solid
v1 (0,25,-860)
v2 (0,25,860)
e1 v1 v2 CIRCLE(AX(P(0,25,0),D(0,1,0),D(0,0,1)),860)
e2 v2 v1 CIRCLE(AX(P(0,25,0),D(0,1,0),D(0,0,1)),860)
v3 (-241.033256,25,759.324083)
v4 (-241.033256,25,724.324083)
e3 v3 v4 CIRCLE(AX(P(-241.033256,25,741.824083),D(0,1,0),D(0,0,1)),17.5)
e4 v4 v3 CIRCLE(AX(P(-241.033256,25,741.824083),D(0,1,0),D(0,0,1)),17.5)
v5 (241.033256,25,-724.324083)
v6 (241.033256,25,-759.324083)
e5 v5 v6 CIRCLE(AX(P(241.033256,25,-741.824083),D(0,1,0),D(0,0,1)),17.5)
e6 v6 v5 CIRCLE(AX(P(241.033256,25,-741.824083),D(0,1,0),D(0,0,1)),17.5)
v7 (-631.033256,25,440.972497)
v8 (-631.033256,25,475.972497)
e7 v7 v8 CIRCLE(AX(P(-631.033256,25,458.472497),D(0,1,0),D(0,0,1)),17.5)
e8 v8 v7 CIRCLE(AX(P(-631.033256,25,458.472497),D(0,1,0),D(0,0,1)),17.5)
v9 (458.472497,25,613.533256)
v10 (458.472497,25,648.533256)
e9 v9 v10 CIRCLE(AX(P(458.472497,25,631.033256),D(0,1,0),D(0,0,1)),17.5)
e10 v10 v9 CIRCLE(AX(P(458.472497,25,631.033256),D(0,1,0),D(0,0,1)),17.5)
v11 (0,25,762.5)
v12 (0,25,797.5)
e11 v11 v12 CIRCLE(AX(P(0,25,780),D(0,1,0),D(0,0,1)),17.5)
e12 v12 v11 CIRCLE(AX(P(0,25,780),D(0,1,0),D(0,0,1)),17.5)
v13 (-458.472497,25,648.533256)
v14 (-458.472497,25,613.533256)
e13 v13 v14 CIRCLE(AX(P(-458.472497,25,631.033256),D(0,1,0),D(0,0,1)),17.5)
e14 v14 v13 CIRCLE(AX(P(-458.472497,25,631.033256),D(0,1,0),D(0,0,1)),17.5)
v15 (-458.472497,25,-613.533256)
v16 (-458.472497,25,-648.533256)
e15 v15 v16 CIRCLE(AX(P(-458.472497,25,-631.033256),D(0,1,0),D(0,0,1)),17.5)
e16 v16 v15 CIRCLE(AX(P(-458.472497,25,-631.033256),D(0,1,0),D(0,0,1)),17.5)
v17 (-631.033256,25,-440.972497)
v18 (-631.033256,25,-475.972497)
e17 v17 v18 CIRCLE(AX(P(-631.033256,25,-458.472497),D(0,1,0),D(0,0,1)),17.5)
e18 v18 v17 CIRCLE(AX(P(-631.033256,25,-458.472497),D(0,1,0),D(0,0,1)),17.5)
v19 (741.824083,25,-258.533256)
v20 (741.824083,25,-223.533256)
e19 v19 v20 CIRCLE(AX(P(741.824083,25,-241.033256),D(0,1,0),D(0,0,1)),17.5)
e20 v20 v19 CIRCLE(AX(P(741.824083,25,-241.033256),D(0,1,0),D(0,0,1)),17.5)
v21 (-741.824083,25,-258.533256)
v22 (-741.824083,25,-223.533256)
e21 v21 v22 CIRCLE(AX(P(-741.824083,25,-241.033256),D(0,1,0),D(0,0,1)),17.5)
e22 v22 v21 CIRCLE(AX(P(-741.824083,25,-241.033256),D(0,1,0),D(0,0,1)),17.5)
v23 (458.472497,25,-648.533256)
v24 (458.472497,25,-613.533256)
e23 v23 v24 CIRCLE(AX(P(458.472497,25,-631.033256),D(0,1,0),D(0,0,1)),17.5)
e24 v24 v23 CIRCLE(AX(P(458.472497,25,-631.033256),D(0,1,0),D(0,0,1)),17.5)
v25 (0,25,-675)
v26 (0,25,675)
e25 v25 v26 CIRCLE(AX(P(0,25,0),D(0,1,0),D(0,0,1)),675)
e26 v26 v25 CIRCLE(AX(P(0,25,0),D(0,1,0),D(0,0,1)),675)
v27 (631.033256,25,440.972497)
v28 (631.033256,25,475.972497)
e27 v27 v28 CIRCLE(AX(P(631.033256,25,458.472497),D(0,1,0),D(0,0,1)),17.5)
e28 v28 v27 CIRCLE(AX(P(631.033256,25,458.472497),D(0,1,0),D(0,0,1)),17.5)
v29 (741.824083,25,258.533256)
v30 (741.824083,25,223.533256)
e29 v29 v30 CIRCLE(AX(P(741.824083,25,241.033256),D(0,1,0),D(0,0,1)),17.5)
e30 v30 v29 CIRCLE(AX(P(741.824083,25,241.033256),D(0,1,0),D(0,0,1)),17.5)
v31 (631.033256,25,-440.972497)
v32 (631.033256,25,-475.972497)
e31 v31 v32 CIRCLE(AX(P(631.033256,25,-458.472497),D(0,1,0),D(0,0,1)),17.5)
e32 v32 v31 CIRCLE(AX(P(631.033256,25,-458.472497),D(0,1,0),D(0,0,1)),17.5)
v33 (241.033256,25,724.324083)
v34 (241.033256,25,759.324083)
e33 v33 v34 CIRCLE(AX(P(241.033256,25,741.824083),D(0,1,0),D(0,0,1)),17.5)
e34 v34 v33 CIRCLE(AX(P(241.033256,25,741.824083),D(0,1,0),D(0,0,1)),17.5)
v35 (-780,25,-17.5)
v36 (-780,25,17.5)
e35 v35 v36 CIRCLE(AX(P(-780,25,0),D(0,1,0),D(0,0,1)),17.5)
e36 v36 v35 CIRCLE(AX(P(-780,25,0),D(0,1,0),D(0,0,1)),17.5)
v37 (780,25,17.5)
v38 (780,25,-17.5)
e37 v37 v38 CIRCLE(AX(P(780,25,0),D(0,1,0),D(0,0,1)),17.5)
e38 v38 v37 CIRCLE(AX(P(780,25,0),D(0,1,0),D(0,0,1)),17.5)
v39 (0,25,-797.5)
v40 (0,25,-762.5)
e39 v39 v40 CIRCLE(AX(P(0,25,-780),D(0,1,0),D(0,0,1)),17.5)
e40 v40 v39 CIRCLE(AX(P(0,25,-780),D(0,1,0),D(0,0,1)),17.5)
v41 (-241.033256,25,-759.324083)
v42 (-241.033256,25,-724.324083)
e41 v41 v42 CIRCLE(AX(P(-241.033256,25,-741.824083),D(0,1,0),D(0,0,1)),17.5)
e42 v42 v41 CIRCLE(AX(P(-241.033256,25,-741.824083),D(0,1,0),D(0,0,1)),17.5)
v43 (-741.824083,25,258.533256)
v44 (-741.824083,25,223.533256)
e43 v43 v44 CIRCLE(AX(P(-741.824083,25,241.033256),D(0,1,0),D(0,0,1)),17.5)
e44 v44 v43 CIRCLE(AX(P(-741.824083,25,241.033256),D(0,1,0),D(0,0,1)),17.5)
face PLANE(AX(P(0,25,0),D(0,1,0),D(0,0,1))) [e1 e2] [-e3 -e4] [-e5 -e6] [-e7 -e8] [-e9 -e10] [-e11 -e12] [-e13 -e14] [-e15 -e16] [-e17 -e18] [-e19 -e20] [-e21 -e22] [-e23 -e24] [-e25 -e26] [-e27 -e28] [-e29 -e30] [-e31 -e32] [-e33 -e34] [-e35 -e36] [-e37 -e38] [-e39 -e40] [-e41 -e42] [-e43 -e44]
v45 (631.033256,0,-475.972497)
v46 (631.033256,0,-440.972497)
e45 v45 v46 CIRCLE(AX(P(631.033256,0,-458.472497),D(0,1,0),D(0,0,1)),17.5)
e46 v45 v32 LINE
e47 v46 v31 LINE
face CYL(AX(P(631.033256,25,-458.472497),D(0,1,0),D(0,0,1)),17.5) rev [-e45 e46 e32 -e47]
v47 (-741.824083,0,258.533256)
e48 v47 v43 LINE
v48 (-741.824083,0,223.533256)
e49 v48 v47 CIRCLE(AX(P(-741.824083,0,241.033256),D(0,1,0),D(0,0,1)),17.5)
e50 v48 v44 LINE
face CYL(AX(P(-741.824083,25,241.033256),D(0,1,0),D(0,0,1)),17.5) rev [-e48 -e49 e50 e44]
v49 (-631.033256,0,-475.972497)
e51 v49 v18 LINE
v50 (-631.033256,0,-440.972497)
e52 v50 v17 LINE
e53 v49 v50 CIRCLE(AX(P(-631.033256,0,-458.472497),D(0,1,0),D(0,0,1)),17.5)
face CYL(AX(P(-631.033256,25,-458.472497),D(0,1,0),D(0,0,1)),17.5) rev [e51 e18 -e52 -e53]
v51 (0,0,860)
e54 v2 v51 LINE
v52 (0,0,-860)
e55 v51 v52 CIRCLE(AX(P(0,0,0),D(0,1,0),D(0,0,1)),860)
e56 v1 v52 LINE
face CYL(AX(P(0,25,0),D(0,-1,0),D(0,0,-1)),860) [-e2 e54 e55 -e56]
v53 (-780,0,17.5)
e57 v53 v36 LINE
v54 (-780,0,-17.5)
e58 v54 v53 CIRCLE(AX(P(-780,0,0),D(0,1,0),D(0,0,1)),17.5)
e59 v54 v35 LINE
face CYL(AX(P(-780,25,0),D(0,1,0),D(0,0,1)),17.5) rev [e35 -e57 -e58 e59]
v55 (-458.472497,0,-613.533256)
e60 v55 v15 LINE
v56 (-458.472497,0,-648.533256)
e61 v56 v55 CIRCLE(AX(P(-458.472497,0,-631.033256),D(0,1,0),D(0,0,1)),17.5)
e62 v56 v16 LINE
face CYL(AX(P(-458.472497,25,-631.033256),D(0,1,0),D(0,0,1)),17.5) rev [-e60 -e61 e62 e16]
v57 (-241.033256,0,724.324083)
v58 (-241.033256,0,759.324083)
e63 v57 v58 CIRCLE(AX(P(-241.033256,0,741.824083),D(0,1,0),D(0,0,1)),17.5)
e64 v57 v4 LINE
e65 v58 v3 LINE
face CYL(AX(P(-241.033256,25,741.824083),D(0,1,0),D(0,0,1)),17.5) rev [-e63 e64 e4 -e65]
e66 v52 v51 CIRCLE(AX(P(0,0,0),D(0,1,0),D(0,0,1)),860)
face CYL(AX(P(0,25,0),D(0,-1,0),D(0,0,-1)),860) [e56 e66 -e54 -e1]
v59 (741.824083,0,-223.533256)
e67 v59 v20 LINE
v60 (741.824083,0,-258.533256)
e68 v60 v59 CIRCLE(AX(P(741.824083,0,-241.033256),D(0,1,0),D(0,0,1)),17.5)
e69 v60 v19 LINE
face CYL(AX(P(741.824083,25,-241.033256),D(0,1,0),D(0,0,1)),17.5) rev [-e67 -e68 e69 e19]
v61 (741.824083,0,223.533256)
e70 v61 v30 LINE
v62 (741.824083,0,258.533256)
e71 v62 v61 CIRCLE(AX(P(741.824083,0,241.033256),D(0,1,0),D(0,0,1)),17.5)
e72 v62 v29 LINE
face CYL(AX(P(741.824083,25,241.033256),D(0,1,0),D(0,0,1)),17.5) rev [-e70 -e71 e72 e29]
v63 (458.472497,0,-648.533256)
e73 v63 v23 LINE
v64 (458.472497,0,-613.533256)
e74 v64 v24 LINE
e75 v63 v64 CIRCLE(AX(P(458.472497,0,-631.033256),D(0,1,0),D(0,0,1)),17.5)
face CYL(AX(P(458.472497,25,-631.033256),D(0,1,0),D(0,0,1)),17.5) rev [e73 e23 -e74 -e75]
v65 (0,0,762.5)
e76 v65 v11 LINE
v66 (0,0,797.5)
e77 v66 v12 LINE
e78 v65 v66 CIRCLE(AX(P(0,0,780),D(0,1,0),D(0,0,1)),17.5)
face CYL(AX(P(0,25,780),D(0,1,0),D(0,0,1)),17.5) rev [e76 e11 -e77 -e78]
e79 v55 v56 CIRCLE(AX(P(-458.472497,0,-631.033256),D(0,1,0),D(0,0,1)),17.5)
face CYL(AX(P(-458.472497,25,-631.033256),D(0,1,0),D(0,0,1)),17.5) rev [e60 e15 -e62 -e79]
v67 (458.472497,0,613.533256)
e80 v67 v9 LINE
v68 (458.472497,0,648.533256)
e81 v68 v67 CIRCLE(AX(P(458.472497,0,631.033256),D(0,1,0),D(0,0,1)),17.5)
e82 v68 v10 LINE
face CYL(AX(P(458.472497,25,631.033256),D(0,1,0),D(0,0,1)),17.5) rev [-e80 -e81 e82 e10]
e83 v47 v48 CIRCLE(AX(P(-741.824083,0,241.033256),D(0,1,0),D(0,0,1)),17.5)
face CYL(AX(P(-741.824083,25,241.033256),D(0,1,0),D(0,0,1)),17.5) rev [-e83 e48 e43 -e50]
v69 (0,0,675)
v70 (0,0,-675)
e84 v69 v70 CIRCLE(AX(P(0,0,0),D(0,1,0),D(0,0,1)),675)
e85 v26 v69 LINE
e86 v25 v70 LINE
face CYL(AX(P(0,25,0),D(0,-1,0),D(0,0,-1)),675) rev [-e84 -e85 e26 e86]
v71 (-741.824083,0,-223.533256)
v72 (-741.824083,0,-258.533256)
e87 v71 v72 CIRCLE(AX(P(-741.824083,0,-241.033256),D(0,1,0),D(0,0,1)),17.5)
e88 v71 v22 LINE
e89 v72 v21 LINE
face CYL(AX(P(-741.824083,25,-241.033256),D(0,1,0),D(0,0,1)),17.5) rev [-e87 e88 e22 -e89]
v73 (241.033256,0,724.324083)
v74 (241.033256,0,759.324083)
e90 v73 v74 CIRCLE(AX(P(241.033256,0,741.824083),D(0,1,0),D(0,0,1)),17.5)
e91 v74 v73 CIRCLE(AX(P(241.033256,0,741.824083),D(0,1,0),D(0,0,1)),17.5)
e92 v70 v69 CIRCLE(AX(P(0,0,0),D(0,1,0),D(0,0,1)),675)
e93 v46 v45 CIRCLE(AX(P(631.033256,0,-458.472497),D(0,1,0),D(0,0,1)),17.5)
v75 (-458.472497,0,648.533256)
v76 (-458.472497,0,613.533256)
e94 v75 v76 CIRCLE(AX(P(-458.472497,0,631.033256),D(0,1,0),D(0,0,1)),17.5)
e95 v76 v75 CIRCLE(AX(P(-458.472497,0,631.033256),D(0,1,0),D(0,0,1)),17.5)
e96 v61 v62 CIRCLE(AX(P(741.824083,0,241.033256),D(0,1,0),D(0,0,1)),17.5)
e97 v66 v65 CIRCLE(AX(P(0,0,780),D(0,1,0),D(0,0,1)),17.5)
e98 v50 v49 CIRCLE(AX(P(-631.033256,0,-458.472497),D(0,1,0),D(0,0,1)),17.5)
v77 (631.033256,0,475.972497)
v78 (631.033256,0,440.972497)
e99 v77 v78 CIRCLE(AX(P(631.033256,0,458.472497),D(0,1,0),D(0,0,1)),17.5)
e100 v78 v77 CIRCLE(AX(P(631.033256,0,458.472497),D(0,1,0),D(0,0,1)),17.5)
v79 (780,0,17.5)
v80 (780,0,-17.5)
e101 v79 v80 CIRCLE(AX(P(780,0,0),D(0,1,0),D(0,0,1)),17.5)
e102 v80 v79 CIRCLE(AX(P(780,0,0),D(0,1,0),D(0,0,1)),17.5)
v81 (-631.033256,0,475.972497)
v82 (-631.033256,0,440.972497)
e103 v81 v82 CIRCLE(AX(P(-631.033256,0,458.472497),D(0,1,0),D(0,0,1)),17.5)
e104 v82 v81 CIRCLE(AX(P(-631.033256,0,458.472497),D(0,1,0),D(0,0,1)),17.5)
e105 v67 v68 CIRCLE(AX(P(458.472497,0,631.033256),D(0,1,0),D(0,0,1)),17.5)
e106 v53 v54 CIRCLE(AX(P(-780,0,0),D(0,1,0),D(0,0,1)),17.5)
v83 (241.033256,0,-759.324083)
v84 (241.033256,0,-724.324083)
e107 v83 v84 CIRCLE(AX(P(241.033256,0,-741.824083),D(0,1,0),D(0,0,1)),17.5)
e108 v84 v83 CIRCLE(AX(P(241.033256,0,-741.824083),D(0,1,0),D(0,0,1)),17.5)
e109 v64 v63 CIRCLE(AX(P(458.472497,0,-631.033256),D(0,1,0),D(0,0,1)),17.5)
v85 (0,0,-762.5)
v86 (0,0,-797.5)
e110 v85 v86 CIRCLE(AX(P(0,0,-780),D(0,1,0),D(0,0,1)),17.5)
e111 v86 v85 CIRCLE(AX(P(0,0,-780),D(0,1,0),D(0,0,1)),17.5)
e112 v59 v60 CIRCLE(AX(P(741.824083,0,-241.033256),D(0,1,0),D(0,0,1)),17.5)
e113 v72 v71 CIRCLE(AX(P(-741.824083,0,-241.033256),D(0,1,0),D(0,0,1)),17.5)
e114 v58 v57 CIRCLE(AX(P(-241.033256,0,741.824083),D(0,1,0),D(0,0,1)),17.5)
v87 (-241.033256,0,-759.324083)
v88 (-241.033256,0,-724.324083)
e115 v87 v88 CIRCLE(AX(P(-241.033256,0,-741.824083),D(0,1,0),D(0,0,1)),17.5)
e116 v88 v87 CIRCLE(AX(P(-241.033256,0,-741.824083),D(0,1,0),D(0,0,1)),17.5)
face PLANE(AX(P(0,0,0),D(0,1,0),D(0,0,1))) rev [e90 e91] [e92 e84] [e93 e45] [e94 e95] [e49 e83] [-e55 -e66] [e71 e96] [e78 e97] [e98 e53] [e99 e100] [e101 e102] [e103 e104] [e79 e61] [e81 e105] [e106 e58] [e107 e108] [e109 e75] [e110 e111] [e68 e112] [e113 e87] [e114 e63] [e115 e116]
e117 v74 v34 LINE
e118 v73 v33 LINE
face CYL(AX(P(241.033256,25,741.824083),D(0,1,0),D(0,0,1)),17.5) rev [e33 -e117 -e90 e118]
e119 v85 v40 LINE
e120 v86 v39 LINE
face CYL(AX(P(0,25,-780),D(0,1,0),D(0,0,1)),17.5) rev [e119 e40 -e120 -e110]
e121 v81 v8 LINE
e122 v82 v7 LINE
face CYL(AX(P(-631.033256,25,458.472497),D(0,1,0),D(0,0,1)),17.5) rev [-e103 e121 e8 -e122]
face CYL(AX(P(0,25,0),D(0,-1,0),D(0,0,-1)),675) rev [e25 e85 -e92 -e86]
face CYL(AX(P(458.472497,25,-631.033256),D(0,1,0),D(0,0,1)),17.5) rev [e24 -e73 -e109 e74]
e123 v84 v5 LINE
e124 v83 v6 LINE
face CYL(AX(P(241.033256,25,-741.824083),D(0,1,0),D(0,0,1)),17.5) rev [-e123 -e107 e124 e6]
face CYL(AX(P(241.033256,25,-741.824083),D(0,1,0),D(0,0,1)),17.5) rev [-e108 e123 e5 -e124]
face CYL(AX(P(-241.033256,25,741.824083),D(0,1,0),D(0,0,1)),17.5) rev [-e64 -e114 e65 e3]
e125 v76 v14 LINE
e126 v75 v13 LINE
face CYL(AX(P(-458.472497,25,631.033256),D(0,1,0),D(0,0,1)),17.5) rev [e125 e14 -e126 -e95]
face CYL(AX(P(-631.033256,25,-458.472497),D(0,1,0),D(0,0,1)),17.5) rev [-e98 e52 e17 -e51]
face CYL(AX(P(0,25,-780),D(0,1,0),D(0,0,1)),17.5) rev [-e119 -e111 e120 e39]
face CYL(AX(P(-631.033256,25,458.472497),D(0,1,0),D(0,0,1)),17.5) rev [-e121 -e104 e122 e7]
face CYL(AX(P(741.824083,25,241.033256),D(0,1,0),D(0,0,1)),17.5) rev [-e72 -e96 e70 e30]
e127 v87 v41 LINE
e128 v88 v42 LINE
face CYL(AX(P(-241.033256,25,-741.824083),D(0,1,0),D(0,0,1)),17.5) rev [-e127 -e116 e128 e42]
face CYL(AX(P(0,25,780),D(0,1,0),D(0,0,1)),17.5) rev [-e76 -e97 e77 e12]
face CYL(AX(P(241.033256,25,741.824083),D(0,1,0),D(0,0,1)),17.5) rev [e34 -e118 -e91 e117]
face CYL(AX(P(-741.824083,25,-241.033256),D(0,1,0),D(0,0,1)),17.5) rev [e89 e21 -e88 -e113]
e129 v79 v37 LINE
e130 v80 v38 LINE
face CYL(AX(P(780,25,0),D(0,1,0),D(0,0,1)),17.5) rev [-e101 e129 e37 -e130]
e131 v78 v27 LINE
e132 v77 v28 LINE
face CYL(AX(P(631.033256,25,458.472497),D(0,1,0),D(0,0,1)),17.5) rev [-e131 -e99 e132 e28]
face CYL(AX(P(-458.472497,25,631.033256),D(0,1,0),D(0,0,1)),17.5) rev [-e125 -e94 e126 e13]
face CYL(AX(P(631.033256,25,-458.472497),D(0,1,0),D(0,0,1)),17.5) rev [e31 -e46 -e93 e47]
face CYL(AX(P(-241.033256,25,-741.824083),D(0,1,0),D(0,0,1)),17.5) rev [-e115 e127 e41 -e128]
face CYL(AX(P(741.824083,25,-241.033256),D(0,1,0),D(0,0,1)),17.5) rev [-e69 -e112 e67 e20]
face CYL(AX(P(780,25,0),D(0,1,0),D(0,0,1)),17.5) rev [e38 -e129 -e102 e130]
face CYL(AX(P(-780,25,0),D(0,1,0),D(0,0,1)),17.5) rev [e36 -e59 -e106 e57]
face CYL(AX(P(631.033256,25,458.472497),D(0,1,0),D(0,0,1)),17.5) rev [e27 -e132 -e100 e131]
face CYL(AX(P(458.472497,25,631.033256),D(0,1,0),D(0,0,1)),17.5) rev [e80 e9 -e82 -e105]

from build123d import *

# Parameters (mm, degrees)
SKETCH_1_R                = 860
SKETCH_1_R_2              = 675
EXTRUDE_1_DEPTH           = 25
HOLE_WIZARD_25_5_25_5_1_D = 35


with BuildPart() as part:
    # 草图1 → 凸台-拉伸1 (new body)
    with BuildSketch(Plane(origin=(0, 0, 0), x_dir=(1, 0, 0), z_dir=(0, 1, 0))):
        with Locations(Location((0, 0, 0), (0, 0, 270))):
            Circle(SKETCH_1_R)
        with Locations(Location((0, 0, 0), (0, 0, 270))):
            Circle(SKETCH_1_R_2, mode=Mode.SUBTRACT)
    extrude(amount=EXTRUDE_1_DEPTH)

    # Ø25.5 (25.5) 直径孔1 (through all)
    with Locations(Plane(origin=(0, 25, 0), x_dir=(1, 0, 0), z_dir=(0, 1, 0))):
        with Locations((0, 780), (241.033255612, 741.82408271), (458.472496788, 631.033255612), (631.033255612, 458.472496788), (741.82408271, 241.033255612), (780, 0), (741.82408271, -241.033255612), (631.033255612, -458.472496788), (458.472496788, -631.033255612), (241.033255612, -741.82408271), (0, -780), (-241.033255612, -741.82408271), (-458.472496788, -631.033255612), (-631.033255612, -458.472496788), (-741.82408271, -241.033255612), (-780, 0), (-741.82408271, 241.033255612), (-631.033255612, 458.472496788), (-458.472496788, 631.033255612), (-241.033255612, 741.82408271)):
            Hole(HOLE_WIZARD_25_5_25_5_1_D / 2)


solid = part.part
